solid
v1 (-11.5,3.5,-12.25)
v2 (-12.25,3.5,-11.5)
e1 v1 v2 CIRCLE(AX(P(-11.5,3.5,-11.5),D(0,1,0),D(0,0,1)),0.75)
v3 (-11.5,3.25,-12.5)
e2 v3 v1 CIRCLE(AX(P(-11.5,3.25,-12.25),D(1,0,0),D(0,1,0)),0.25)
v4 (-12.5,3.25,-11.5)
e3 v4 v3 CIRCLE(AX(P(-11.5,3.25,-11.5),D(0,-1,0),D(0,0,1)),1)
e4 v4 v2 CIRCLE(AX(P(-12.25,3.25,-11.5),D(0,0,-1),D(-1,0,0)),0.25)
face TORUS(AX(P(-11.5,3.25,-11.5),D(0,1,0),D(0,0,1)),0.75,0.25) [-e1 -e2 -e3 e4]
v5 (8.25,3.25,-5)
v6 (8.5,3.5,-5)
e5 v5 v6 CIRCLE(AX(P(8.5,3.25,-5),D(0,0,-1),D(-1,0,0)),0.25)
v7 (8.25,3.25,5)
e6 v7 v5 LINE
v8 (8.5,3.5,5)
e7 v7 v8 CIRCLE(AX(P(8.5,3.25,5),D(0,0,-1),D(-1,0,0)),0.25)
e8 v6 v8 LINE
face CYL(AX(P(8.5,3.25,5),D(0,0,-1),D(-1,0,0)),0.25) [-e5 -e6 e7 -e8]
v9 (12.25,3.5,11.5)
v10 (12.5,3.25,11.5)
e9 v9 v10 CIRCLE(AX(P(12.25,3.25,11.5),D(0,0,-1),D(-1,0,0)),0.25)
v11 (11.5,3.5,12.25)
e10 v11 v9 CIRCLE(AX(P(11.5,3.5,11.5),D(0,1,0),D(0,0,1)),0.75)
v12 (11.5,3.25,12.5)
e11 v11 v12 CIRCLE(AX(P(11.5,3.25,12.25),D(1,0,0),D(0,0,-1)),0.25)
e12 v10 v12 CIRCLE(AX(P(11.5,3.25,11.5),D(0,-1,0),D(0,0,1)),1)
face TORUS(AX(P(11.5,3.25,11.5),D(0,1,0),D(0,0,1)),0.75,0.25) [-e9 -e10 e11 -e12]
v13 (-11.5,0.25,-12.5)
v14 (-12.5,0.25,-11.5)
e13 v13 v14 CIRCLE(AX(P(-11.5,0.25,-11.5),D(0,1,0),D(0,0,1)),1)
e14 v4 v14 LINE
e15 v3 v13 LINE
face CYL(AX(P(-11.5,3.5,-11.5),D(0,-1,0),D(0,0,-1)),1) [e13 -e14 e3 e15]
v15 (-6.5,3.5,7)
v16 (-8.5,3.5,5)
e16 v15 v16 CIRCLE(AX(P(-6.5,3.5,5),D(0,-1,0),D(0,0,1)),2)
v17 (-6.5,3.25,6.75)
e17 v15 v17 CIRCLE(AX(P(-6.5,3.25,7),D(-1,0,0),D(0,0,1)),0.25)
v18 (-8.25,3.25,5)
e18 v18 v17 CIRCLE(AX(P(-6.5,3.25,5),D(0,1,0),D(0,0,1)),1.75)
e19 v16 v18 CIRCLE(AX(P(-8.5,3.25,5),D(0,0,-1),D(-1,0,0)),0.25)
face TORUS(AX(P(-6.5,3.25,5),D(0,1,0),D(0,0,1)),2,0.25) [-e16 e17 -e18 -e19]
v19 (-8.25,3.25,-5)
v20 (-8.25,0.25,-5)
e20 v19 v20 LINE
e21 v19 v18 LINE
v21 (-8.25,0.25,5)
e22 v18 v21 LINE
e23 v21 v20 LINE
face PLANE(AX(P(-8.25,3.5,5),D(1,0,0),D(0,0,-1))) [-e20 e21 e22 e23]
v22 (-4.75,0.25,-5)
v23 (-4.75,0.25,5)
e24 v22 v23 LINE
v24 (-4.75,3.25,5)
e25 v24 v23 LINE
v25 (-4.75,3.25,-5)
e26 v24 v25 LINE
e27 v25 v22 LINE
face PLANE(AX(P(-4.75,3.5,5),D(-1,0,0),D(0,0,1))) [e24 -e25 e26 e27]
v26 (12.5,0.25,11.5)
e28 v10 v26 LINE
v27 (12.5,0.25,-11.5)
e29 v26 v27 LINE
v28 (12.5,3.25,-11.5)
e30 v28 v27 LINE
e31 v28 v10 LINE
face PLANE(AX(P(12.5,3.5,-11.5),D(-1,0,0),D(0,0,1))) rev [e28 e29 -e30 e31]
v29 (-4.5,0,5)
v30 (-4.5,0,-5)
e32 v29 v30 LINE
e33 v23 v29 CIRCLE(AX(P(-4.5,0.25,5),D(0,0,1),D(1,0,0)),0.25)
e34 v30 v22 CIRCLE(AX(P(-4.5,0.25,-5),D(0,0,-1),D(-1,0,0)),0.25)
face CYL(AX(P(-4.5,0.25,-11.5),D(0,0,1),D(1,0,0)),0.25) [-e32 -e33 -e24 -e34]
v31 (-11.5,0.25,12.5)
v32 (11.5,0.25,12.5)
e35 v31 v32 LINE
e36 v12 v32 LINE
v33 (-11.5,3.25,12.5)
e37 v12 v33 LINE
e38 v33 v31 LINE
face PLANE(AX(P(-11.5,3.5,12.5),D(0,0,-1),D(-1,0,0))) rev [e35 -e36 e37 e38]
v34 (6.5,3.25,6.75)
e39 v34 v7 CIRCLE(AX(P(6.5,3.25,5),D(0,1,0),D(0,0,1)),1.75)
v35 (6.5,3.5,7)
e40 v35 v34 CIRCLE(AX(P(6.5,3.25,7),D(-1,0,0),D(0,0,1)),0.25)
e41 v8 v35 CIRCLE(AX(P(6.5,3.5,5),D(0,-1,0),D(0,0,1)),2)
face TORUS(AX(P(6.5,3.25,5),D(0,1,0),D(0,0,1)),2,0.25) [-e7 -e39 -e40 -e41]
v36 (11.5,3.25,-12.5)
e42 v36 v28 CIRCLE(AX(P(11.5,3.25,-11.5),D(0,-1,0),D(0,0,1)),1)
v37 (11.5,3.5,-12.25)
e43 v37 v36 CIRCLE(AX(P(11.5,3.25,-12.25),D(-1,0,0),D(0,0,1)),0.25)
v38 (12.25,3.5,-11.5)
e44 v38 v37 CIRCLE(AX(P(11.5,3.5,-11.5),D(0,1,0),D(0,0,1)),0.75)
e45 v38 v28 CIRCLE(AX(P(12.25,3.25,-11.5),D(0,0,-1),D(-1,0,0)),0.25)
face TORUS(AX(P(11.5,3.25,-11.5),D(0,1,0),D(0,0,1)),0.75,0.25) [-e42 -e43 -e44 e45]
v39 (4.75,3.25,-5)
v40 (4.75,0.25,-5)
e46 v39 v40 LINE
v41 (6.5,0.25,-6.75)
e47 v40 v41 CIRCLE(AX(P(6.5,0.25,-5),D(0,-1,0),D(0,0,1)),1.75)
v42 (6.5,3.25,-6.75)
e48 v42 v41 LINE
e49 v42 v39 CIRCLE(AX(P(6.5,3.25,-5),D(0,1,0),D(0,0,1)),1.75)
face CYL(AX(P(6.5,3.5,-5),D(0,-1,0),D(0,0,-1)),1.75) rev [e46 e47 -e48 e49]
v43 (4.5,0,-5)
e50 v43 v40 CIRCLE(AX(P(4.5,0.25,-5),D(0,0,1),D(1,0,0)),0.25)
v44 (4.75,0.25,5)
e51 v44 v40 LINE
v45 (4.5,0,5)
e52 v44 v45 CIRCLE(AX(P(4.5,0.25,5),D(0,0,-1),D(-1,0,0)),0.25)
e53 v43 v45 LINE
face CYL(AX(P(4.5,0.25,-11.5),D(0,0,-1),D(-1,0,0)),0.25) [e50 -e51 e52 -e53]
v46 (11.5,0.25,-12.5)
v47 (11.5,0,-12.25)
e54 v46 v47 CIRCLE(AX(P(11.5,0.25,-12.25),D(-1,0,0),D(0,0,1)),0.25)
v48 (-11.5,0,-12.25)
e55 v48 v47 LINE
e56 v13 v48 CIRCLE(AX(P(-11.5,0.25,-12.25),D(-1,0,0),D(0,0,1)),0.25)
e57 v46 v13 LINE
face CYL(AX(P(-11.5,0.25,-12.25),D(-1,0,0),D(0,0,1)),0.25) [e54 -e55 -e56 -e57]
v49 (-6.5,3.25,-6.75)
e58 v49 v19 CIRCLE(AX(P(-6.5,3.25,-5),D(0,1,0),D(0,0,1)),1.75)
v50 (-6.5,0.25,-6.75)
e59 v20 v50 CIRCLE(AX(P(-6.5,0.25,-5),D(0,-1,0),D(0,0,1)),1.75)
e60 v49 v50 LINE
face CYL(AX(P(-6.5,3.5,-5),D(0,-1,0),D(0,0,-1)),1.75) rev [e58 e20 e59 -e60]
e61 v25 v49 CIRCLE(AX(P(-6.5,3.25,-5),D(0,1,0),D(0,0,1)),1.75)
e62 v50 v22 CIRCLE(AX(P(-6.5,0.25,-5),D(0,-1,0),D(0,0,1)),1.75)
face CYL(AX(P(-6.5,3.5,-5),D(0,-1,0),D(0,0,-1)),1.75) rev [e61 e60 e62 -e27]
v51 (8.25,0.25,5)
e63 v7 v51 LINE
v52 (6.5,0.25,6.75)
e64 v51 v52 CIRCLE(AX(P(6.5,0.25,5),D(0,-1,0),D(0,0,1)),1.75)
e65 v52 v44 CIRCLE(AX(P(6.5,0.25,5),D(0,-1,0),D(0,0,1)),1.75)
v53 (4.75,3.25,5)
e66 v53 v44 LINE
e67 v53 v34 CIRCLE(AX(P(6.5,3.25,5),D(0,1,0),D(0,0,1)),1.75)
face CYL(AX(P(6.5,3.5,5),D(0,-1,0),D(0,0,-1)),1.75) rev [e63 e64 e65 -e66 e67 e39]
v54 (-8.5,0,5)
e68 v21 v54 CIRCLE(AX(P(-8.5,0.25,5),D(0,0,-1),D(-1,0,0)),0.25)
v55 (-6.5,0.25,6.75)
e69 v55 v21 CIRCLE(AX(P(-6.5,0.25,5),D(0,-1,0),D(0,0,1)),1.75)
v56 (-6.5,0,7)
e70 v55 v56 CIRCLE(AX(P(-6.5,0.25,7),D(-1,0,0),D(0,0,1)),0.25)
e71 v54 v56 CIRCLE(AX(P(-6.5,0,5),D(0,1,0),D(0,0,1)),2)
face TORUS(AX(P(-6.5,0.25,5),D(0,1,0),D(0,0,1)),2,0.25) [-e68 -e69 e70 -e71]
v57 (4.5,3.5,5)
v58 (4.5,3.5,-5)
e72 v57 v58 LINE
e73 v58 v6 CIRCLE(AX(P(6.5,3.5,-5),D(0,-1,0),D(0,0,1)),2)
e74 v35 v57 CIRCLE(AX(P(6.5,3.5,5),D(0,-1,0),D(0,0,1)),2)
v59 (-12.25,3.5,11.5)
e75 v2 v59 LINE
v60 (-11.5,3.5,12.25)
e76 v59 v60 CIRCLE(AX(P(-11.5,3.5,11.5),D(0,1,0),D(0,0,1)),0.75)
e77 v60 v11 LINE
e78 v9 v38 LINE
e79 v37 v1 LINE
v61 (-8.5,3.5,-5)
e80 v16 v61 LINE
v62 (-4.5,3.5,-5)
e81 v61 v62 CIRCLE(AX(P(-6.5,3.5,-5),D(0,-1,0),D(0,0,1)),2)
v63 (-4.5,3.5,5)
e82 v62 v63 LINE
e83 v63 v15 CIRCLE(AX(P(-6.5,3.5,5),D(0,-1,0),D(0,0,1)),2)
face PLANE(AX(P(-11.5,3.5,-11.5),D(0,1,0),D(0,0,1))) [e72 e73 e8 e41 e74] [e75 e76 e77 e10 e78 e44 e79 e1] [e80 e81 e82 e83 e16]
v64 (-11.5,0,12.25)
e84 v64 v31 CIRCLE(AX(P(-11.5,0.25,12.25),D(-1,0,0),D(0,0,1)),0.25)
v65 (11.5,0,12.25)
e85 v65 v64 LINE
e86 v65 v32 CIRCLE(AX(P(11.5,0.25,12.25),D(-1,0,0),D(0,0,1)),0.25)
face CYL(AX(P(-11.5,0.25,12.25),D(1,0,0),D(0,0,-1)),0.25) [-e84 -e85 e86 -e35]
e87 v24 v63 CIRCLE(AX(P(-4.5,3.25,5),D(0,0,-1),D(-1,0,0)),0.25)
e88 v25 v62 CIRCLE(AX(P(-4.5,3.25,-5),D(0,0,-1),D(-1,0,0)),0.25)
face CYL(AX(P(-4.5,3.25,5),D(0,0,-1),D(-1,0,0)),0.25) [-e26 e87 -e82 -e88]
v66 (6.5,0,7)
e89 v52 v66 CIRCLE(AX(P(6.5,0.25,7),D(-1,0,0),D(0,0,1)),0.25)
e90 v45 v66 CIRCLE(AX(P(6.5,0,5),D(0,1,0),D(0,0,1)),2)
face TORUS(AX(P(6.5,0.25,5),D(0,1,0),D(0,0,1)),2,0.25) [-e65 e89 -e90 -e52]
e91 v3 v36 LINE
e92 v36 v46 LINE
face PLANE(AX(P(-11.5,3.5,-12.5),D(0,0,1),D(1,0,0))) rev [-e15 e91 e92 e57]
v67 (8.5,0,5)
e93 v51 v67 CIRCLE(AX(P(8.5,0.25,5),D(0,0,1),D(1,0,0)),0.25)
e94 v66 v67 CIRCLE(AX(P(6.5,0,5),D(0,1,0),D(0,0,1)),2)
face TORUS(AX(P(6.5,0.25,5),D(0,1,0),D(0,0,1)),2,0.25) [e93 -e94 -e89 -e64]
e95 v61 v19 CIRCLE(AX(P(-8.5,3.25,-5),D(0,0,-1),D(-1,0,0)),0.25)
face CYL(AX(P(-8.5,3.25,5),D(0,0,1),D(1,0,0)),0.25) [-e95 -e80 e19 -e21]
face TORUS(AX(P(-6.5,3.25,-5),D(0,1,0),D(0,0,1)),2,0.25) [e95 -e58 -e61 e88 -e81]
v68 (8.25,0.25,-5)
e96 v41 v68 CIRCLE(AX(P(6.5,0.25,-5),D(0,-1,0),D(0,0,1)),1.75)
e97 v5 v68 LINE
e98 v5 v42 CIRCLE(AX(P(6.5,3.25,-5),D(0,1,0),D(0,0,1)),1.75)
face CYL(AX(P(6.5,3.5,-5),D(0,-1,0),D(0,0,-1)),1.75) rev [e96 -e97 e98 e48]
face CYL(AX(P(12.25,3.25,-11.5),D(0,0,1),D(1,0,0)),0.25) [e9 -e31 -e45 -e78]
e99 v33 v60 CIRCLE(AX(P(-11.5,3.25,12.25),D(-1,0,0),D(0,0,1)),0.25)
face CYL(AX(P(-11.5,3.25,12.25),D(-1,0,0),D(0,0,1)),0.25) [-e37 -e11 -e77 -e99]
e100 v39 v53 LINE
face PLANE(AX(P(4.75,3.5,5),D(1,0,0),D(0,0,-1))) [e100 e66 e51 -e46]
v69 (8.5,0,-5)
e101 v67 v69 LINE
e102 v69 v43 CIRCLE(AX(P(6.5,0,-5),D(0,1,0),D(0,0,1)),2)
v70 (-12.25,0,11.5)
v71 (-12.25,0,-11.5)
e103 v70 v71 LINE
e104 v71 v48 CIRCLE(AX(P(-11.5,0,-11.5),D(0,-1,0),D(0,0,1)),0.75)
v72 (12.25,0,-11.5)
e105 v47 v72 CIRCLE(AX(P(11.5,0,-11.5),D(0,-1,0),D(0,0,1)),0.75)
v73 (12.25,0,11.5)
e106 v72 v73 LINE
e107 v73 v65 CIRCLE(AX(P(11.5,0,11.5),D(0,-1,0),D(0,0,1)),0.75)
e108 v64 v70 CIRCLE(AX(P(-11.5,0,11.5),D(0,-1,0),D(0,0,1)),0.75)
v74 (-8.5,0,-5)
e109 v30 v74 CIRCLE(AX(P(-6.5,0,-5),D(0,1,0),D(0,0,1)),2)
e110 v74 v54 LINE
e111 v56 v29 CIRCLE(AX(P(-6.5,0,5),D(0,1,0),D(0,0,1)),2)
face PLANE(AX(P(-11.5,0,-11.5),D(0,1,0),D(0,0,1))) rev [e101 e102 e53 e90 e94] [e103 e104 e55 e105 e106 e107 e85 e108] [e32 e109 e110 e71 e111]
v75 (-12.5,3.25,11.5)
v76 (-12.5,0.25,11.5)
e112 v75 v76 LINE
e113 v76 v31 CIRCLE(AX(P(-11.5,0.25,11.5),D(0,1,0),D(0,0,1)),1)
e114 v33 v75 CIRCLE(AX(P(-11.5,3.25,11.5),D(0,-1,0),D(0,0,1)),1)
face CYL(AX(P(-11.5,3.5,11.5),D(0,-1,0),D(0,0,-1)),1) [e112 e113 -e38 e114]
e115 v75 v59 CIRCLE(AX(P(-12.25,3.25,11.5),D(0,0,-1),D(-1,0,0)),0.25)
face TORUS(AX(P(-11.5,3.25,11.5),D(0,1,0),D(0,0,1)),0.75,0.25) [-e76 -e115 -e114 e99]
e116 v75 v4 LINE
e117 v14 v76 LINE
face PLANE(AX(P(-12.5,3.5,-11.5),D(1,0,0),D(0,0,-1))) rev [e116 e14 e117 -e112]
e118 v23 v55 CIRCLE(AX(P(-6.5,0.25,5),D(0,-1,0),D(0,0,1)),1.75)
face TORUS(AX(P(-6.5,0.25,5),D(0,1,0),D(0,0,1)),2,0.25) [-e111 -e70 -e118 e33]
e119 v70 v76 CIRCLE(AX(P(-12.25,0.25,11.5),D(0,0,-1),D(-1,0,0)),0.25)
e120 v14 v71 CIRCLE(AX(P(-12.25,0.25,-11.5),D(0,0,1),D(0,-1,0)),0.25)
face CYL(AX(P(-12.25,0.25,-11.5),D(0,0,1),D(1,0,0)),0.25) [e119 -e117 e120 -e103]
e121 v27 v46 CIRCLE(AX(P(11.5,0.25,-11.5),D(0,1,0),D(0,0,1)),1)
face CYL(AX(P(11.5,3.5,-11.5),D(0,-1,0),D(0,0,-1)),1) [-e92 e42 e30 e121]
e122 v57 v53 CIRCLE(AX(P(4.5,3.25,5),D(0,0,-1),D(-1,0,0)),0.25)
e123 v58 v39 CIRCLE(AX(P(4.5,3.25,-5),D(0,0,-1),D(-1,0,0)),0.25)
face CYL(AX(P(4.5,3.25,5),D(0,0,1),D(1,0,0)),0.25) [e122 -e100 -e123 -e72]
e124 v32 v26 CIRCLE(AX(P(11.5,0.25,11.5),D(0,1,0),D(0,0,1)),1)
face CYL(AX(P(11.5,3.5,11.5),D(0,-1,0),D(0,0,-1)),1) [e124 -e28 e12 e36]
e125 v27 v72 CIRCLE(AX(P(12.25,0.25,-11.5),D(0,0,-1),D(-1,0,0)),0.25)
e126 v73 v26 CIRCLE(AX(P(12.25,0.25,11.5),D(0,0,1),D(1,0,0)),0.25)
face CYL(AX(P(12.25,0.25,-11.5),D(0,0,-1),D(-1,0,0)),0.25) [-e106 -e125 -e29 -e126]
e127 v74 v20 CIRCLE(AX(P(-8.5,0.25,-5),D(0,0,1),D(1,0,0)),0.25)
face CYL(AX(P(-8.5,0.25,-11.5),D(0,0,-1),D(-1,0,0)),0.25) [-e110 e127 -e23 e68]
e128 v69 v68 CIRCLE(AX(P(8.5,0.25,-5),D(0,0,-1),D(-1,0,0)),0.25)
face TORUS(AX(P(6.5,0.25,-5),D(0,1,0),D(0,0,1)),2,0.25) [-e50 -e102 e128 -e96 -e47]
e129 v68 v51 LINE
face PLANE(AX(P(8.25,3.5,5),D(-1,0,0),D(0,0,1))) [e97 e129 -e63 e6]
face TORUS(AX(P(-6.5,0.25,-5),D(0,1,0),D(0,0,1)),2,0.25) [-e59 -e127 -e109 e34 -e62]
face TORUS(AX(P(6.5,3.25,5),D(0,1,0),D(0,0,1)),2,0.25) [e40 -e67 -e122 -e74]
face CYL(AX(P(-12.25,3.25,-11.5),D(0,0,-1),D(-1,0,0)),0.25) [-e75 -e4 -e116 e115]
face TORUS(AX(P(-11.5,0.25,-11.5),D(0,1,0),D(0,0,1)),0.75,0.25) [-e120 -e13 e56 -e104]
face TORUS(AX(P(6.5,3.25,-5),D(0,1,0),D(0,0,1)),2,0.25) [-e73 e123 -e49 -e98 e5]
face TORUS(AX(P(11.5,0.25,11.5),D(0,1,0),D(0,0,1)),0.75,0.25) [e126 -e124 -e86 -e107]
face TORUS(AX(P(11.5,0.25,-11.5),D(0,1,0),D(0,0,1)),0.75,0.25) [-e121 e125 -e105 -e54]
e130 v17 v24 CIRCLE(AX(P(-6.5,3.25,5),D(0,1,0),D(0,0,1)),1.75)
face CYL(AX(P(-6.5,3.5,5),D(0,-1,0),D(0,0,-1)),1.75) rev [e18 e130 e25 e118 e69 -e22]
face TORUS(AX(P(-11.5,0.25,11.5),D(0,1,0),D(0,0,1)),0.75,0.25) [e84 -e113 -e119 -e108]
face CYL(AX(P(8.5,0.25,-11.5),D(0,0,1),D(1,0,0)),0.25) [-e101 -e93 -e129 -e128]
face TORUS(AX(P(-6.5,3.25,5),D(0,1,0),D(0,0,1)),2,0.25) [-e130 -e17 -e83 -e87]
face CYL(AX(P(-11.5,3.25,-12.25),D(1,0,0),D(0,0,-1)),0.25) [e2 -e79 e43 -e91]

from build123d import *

# Parameters (mm, degrees)
BOSS_EXTRUDE1_DEPTH = 3.5
FILLET1_R           = 0.25


with BuildPart() as part:
    # Sketch1 → Boss-Extrude1 (new body)
    with BuildSketch(Plane(origin=(0, 0, 0), x_dir=(1, 0, 0), z_dir=(0, 1, 0))):
        with BuildLine():
            Line((-11.5, 12.5), (11.5, 12.5))
            ThreePointArc((11.5, 12.5), (12.207106781, 12.207106781), (12.5, 11.5))
            Line((12.5, 11.5), (12.5, -11.5))
            ThreePointArc((12.5, -11.5), (12.207106781, -12.207106781), (11.5, -12.5))
            Line((11.5, -12.5), (-11.5, -12.5))
            ThreePointArc((-11.5, -12.5), (-12.207106781, -12.207106781), (-12.5, -11.5))
            Line((-12.5, -11.5), (-12.5, 11.5))
            ThreePointArc((-12.5, 11.5), (-12.207106781, 12.207106781), (-11.5, 12.5))
        make_face()
        with BuildLine():
            Line((-8.25, -5), (-8.25, 5))
            ThreePointArc((-8.25, 5), (-6.5, 6.75), (-4.75, 5))
            Line((-4.75, 5), (-4.75, -5))
            ThreePointArc((-4.75, -5), (-6.5, -6.75), (-8.25, -5))
        make_face(mode=Mode.SUBTRACT)
        with BuildLine():
            Line((8.25, -5), (8.25, 5))
            ThreePointArc((8.25, 5), (6.5, 6.75), (4.75, 5))
            Line((4.75, 5), (4.75, -5))
            ThreePointArc((4.75, -5), (6.5, -6.75), (8.25, -5))
        make_face(mode=Mode.SUBTRACT)
    extrude(amount=BOSS_EXTRUDE1_DEPTH)

    # Fillet1
    fillet1_edges = [part.edges().sort_by_distance(p)[0] for p in [
        (0, 0, 12.5),
        (-12.207106781, 0, 12.207106781),
        (-12.5, 0, 0),
        (-12.207106781, 0, -12.207106781),
        (-12.207106781, 3.5, 12.207106781),
        (0, 3.5, 12.5),
        (12.207106781, 3.5, 12.207106781),
        (-6.5, 0, 6.75),
        (-4.75, 0, 0),
        (12.5, 3.5, 0),
        (-6.5, 0, -6.75),
        (-8.25, 0, 0),
        (-6.5, 3.5, 6.75),
        (-4.75, 3.5, 0),
        (-6.5, 3.5, -6.75),
        (-8.25, 3.5, 0),
        (12.207106781, 3.5, -12.207106781),
        (0, 3.5, -12.5),
        (6.5, 0, 6.75),
        (8.25, 0, 0),
        (6.5, 0, -6.75),
        (4.75, 0, 0),
        (6.5, 3.5, 6.75),
        (8.25, 3.5, 0),
        (6.5, 3.5, -6.75),
        (4.75, 3.5, 0),
        (-12.207106781, 3.5, -12.207106781),
        (0, 0, -12.5),
        (-12.5, 3.5, 0),
        (12.207106781, 0, -12.207106781),
        (12.5, 0, 0),
        (12.207106781, 0, 12.207106781),
    ]]
    fillet(fillet1_edges, radius=FILLET1_R)


solid = part.part
